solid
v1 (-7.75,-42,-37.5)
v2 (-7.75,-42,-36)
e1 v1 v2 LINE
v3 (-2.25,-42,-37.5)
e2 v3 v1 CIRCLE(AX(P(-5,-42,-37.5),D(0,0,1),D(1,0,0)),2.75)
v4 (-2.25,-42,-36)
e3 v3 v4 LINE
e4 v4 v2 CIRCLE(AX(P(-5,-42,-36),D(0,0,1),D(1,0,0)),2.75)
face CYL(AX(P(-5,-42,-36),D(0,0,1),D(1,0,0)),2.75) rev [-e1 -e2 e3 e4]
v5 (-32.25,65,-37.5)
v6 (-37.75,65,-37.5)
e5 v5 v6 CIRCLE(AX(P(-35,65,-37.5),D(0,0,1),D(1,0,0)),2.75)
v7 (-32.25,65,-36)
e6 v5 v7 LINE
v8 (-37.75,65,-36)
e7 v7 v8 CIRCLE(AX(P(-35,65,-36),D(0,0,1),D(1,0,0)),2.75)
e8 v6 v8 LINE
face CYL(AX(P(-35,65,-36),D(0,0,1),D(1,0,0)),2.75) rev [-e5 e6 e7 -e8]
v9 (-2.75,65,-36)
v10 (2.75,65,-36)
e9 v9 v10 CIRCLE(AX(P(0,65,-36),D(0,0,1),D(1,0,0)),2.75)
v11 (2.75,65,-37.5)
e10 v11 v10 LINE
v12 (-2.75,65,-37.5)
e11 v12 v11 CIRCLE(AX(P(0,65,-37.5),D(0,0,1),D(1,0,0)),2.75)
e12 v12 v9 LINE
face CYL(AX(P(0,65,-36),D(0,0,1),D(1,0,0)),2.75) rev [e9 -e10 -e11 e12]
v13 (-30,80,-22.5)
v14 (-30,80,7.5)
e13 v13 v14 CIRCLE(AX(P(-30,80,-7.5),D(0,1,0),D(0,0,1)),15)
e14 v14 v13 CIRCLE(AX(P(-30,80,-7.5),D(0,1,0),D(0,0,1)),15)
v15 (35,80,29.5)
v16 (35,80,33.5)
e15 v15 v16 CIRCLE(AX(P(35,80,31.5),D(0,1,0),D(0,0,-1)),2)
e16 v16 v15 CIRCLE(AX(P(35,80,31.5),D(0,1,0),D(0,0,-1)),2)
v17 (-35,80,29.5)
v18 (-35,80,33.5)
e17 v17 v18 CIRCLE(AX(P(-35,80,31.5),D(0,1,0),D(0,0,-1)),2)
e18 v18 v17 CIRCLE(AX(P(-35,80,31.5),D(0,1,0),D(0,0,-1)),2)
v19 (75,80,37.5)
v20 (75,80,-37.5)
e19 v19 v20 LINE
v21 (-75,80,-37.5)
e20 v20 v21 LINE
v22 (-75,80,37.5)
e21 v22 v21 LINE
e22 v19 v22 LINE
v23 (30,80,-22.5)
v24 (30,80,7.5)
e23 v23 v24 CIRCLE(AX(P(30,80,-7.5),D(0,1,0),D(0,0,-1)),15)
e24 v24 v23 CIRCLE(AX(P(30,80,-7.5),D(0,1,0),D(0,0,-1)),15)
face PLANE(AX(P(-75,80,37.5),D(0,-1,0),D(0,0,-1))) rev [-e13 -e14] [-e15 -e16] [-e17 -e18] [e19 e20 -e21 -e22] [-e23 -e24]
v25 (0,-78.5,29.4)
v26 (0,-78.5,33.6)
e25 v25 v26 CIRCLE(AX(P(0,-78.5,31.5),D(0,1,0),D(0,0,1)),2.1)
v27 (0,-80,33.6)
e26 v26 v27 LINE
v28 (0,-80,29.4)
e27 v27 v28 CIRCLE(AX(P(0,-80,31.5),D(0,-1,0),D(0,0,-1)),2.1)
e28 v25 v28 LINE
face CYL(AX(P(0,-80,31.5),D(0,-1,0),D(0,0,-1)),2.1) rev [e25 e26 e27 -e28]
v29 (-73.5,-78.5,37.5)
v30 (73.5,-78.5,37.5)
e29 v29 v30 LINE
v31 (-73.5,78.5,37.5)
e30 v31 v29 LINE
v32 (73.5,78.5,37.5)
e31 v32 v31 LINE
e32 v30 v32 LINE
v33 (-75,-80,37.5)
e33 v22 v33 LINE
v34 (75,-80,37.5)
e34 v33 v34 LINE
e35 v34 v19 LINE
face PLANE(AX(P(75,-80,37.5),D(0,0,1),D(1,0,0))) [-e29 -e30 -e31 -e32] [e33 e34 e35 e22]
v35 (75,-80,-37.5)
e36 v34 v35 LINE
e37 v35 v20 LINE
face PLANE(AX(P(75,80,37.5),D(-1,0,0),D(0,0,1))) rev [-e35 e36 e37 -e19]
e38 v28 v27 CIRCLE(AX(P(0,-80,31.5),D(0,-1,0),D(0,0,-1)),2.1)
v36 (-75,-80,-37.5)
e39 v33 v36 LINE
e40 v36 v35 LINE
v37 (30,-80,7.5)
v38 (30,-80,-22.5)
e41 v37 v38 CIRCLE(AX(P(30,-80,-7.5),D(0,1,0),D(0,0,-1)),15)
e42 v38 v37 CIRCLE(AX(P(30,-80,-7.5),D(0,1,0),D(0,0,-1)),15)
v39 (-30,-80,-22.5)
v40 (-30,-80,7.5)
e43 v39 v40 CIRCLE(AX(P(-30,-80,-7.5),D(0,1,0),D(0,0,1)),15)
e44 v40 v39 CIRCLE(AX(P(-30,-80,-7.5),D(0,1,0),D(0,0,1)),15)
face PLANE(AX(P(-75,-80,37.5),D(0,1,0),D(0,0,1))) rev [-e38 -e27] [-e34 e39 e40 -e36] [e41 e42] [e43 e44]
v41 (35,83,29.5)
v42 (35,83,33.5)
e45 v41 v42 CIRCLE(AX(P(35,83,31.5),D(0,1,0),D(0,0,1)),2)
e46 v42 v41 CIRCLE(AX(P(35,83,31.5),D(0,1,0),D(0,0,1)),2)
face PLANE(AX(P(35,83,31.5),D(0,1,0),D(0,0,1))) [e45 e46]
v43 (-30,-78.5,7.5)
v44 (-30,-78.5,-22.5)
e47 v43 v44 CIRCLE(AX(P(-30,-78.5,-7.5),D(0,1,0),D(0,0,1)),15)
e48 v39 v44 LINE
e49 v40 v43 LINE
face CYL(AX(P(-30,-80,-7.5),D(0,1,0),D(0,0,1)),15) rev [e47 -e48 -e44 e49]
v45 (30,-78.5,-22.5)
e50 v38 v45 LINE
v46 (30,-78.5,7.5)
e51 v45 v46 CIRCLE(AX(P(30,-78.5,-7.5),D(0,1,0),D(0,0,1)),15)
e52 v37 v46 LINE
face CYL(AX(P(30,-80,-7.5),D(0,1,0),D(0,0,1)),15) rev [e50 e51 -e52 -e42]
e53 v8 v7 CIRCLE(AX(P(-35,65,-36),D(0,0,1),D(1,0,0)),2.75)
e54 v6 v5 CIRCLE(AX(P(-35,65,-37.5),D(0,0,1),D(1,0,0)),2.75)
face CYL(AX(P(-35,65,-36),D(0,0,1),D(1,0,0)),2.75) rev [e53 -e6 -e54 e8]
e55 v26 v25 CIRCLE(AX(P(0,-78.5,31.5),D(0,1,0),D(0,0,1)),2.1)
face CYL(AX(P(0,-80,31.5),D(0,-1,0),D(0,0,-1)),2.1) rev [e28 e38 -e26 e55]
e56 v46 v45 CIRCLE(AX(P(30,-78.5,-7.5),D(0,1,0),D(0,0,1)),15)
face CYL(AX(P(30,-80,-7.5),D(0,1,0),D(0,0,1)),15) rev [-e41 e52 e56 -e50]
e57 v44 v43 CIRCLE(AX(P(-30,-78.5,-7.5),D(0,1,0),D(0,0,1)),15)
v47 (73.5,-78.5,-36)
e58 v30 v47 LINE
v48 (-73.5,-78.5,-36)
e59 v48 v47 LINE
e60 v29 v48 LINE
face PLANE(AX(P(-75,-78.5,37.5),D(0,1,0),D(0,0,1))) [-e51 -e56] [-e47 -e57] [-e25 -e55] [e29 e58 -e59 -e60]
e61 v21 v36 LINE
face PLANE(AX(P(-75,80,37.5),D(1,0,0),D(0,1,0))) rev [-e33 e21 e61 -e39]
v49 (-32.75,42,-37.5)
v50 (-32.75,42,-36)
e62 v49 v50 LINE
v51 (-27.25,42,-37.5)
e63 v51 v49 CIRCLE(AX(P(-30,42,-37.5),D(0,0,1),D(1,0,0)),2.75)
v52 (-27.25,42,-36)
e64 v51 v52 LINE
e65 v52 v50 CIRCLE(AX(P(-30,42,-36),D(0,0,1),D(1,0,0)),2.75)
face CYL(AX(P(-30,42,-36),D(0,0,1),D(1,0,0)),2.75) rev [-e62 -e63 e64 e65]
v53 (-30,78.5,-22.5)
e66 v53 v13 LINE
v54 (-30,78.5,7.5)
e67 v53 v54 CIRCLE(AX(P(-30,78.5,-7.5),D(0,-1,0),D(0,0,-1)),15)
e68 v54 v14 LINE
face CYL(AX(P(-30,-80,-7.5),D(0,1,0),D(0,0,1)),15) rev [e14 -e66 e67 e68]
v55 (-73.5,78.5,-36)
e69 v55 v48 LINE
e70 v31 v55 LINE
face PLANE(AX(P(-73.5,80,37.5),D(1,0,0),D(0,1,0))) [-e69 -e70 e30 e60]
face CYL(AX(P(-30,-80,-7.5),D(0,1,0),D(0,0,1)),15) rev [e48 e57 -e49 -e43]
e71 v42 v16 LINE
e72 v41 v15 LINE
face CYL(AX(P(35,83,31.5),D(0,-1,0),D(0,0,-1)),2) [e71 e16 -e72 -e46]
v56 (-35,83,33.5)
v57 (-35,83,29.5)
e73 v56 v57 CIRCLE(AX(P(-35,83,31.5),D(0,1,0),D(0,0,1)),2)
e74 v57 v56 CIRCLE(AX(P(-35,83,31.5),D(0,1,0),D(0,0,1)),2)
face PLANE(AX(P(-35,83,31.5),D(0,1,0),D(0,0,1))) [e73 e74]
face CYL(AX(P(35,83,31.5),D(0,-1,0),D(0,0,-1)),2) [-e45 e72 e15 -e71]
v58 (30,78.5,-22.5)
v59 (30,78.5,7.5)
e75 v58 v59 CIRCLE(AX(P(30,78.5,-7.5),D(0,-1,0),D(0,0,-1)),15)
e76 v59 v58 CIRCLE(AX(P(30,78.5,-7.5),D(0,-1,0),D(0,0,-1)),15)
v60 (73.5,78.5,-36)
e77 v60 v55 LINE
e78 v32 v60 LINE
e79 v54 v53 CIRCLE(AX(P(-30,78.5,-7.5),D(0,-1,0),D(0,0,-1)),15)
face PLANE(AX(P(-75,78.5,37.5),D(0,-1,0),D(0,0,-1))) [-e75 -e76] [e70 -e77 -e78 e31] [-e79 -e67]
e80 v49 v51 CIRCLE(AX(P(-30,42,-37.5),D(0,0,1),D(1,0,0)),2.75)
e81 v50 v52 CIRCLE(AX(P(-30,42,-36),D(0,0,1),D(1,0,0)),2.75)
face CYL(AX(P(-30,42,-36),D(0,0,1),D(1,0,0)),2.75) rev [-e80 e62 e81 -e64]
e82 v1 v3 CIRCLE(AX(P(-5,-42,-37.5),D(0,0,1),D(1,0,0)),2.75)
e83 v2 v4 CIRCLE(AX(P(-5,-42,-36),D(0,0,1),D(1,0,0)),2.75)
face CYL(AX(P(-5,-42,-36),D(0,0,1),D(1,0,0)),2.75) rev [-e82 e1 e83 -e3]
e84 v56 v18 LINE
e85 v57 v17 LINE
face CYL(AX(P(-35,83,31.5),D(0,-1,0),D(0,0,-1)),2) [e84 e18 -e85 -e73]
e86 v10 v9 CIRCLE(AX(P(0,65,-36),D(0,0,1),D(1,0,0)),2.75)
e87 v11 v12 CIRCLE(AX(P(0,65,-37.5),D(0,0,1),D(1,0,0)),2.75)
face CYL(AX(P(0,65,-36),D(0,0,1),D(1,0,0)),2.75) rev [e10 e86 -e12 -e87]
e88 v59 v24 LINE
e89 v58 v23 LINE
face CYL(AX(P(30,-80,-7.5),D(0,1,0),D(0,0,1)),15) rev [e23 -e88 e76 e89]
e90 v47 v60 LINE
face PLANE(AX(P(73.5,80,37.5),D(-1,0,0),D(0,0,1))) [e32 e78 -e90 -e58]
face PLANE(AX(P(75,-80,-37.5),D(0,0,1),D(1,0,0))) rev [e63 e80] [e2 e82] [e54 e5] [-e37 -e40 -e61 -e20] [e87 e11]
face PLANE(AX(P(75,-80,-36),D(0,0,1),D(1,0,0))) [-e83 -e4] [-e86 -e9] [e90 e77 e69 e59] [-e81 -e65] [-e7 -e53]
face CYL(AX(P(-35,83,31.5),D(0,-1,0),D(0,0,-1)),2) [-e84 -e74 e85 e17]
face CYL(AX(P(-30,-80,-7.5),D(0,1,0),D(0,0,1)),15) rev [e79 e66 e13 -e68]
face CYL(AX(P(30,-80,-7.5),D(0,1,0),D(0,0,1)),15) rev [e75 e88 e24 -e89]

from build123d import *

# Parameters (mm, degrees)
SKETCH1_W                      = 150
SKETCH1_H                      = 160
BOSS_EXTRUDE1_DEPTH            = 37.5
SHELL1_T                       = -1.5
F_5_5_5_5_DIAMETER_HOLE2_D     = 5.5
SKETCH6_R                      = 15
CUT_EXTRUDE2_DEPTH             = 181.641218995
SKETCH8_R                      = 2
BOSS_EXTRUDE2_DEPTH            = 3
M5_TAPPED_HOLE1_D              = 4.2
M5_TAPPED_HOLE1_DEPTH          = 14
M5_TAPPED_HOLE1_TIP            = 1.2618073
F_5_5_5_5_DIAMETER_HOLE1_D     = 5.5
F_5_5_5_5_DIAMETER_HOLE1_DEPTH = 15
F_5_5_5_5_DIAMETER_HOLE1_TIP   = 1.652366702


with BuildPart() as part:
    # Sketch1 → Boss-Extrude1 (new, symmetric)
    with BuildSketch(Plane.XY):
        Rectangle(SKETCH1_W, SKETCH1_H)
    extrude(amount=BOSS_EXTRUDE1_DEPTH, both=True)

    # Shell1
    shell1_openings = [part.faces().sort_by_distance(p)[0] for p in [
        (0, 0, 37.5),
    ]]
    offset(amount=SHELL1_T, openings=shell1_openings, kind=Kind.INTERSECTION)

    # Ø5.5 (5.5) Diameter Hole2 (through all)
    with Locations(Plane.XY.offset(-36)):
        with Locations((-30, 42), (-5, -42)):
            Hole(F_5_5_5_5_DIAMETER_HOLE2_D / 2)

    # Sketch6 → Cut-Extrude2 (cut, through all)
    with BuildSketch(Plane(origin=(0, 80, 0), x_dir=(1, 0, 0), z_dir=(0, 1, 0))):
        with Locations(Location((-30, 7.5, 0), (0, 0, 270))):
            Circle(SKETCH6_R)
        with Locations(Location((30, 7.5, 0), (0, 0, 270))):
            Circle(SKETCH6_R)
    extrude(amount=-CUT_EXTRUDE2_DEPTH, mode=Mode.SUBTRACT)

    # Sketch8 → Boss-Extrude2 (add)
    with BuildSketch(Plane(origin=(0, 80, 0), x_dir=(1, 0, 0), z_dir=(0, 1, 0))):
        with Locations(Location((-35, -31.5, 0), (0, 0, 90))):
            Circle(SKETCH8_R)
        with Locations(Location((35, -31.5, 0), (0, 0, 90))):
            Circle(SKETCH8_R)
    extrude(amount=BOSS_EXTRUDE2_DEPTH)

    # M5 Tapped Hole1
    with Locations(Plane.XZ.offset(80)):
        with Locations((0, 31.5)):
            Hole(M5_TAPPED_HOLE1_D / 2, depth=M5_TAPPED_HOLE1_DEPTH)
            with Locations((0, 0, -(M5_TAPPED_HOLE1_DEPTH + M5_TAPPED_HOLE1_TIP / 2))):  # 118° drill point
                Cone(0, M5_TAPPED_HOLE1_D / 2, M5_TAPPED_HOLE1_TIP, mode=Mode.SUBTRACT)

    # Ø5.5 (5.5) Diameter Hole1
    with Locations(Plane.XY.offset(-36)):
        with Locations((0, 65), (-35, 65)):
            Hole(F_5_5_5_5_DIAMETER_HOLE1_D / 2, depth=F_5_5_5_5_DIAMETER_HOLE1_DEPTH)
            with Locations((0, 0, -(F_5_5_5_5_DIAMETER_HOLE1_DEPTH + F_5_5_5_5_DIAMETER_HOLE1_TIP / 2))):  # 118° drill point
                Cone(0, F_5_5_5_5_DIAMETER_HOLE1_D / 2, F_5_5_5_5_DIAMETER_HOLE1_TIP, mode=Mode.SUBTRACT)


solid = part.part
